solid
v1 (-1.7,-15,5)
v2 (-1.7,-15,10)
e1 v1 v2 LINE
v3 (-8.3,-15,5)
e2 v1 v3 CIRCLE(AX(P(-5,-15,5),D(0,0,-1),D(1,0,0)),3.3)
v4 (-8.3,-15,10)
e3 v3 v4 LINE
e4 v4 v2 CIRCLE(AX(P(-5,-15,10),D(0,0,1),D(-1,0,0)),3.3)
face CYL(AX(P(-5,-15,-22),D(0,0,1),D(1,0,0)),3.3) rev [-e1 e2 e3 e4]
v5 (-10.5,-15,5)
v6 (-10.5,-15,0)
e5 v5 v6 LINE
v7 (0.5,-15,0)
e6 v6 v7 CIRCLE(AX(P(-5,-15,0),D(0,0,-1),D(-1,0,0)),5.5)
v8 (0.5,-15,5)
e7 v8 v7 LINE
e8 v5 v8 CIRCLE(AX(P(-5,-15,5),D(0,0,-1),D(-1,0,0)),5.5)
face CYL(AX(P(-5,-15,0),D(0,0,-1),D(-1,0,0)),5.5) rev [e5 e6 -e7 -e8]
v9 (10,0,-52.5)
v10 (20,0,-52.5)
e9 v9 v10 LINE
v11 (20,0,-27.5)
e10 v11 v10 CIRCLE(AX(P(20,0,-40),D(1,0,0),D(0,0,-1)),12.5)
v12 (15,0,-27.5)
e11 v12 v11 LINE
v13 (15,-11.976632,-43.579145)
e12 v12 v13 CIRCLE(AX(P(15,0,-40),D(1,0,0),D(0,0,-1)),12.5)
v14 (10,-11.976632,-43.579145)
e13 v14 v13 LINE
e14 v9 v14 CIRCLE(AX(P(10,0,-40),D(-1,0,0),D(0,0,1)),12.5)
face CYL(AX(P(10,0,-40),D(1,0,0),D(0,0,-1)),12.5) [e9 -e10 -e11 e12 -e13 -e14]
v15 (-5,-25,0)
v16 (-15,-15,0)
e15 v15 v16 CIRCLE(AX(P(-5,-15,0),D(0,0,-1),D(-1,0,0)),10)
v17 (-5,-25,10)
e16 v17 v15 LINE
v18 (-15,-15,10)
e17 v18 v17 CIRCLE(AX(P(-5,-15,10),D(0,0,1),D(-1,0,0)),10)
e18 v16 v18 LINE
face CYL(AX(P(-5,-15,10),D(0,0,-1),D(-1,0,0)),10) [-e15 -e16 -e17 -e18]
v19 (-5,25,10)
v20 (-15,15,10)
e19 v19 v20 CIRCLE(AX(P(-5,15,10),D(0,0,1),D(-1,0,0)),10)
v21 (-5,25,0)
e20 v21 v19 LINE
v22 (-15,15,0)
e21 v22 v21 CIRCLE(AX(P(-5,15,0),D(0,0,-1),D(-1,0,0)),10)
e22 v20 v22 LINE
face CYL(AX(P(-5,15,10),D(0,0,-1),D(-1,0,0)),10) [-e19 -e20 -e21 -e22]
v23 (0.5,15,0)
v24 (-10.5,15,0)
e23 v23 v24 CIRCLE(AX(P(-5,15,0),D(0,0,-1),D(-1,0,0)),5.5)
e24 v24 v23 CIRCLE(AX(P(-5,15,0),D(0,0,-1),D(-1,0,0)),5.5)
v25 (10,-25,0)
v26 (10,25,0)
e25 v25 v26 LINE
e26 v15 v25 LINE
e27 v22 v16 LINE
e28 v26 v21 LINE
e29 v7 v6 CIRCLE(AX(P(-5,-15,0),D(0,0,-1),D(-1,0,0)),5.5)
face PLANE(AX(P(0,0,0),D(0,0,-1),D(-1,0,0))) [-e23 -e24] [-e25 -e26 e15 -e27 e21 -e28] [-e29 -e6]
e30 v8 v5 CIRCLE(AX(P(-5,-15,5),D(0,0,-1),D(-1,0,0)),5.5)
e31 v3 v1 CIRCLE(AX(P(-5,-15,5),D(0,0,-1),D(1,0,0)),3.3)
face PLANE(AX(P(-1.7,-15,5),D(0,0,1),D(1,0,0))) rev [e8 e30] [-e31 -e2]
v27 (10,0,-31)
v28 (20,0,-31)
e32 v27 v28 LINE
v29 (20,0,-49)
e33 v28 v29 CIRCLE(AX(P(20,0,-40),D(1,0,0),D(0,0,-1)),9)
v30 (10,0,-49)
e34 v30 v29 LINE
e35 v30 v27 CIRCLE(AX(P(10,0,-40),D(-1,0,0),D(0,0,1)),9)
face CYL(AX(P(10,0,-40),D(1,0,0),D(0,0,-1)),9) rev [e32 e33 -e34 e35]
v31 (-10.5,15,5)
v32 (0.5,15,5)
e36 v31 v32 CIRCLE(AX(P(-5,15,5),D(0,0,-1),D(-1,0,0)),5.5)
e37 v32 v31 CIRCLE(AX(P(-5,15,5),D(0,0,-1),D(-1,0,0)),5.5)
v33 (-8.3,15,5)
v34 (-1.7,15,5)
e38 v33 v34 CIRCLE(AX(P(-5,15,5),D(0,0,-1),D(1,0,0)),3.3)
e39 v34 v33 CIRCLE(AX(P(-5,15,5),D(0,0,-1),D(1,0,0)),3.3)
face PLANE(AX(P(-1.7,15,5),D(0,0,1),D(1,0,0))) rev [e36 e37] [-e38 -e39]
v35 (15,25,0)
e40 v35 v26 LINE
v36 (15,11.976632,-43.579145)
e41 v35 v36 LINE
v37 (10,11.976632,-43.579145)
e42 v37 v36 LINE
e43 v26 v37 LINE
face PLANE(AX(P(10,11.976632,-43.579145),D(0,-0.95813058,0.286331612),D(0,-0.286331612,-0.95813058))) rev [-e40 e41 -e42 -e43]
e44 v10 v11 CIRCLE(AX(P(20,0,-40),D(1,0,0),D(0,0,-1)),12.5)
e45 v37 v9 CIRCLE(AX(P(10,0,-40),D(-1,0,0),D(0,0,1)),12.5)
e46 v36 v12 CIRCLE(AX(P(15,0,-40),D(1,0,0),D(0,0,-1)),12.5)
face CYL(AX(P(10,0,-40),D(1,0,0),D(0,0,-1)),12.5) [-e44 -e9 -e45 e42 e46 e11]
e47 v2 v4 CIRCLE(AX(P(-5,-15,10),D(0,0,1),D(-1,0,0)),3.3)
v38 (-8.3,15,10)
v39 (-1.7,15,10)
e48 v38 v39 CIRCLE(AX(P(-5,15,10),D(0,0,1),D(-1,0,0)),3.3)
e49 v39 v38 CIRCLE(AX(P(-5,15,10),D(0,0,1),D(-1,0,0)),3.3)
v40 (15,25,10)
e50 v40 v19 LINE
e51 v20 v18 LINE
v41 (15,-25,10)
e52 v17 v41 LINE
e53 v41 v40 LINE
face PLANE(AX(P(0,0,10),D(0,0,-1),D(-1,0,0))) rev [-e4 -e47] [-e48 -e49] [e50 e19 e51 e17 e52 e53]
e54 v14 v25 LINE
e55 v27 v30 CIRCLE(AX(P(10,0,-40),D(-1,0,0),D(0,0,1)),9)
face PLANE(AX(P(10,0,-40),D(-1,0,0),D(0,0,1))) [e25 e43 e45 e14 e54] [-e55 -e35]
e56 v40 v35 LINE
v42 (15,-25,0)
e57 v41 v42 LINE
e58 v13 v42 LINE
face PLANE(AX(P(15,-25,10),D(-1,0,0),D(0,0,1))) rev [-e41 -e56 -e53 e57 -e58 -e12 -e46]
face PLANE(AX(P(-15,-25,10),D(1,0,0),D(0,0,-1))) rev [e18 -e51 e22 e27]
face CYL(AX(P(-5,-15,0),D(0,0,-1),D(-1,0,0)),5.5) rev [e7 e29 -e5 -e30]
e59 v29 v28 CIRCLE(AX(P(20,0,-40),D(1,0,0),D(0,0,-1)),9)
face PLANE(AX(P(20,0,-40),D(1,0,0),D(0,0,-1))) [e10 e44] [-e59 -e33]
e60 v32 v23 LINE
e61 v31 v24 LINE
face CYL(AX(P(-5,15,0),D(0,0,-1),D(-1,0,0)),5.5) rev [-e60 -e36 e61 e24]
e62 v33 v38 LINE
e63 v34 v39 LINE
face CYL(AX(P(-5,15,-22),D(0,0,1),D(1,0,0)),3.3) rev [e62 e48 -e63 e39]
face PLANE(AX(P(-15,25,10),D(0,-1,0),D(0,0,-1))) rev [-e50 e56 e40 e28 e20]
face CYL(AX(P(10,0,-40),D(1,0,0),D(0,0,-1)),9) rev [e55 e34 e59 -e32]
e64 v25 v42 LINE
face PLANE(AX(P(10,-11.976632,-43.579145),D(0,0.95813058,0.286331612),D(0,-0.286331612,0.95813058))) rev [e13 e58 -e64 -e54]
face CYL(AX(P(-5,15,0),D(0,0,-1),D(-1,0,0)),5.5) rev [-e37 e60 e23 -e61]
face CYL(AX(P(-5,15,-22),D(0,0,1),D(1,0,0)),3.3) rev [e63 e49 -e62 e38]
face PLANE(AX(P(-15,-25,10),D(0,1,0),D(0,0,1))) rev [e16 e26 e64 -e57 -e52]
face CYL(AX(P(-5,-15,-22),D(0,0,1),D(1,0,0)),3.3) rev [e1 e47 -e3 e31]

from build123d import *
from build123d.topology import SkipClean

# Parameters (mm, degrees)
SKETCH1_W                                    = 30
SKETCH1_H                                    = 50
BOSS_EXTRUDE1_DEPTH                          = 10
SKETCH2_R                                    = 9
BOSS_EXTRUDE3_DEPTH                          = 5
BOSS_EXTRUDE4_START                          = 5
SKETCH3_R                                    = 12.5
SKETCH3_R_2                                  = 9
BOSS_EXTRUDE4_DEPTH                          = 5
FILLET1_R                                    = 10
CBORE_FOR_M6_HEXAGON_SOCKET_HEAD_CAP_2_COUNT = 2
CBORE_FOR_M6_HEXAGON_SOCKET_HEAD_CAP_2_PITCH = 30
CUT_EXTRUDE1_DEPTH                           = 27
CUT_EXTRUDE1_DEPTH_BACK                      = 19
SKETCH8_R                                    = 3.3


with BuildPart() as part:
    # Sketch1 → Boss-Extrude1 (new body)
    with BuildSketch(Plane.XY):
        Rectangle(SKETCH1_W, SKETCH1_H)
    extrude(amount=BOSS_EXTRUDE1_DEPTH)

    # Sketch2 → Boss-Extrude3 (add)
    with BuildSketch(Plane(origin=(15, -15, 0), x_dir=(0, 1, 0), z_dir=(-1, 0, 0))):
        with BuildLine():
            Line((3.023367754, 43.579145154), (-10, 0))
            Line((-10, 0), (40, 0))
            Line((40, 0), (26.976632246, 43.579145154))
            ThreePointArc((26.976632246, 43.579145154), (15, 52.5), (3.023367754, 43.579145154))
        make_face()
        with Locations(Location((15, 40, 0), (0, 0, 270))):
            Circle(SKETCH2_R, mode=Mode.SUBTRACT)
    extrude(amount=BOSS_EXTRUDE3_DEPTH)

    # Sketch3 → Boss-Extrude4 (add)
    with SkipClean():  # the faces are left unmerged after this step: merging them gives an invalid solid
        with BuildSketch(Plane(origin=(15, 0, 0), x_dir=(0, 0, -1), z_dir=(1, 0, 0)).offset(BOSS_EXTRUDE4_START)):
            with Locations((40, 0)):
                Circle(SKETCH3_R)
            with Locations((40, 0)):
                Circle(SKETCH3_R_2, mode=Mode.SUBTRACT)
        extrude(amount=-BOSS_EXTRUDE4_DEPTH)

    # Fillet1
    fillet1_edges = [part.edges().sort_by_distance(p)[0] for p in [
        (-15, -25, 5),
        (-15, 25, 5),
    ]]
    fillet(fillet1_edges, radius=FILLET1_R)

    # Sketch4 → CBORE for M6 Hexagon socket head cap screws1 (revolve, cut)
    with BuildSketch(Plane(origin=(-5, -15, 0), x_dir=(0, 1, 0), z_dir=(1, 0, 0))):
        Polygon((0, 0), (0, 5), (3.3, 3.017159957), (3.3, 5), (5.5, 5), (5.5, 0), align=None)
    cbore_for_m6_hexagon_socket_head_cap_scr = revolve(axis=Axis((-5, -15, -6.35), (0, 0, 1)), mode=Mode.SUBTRACT)

    # CBORE for M6 Hexagon socket head cap 2: CBORE for M6 Hexagon socket head cap screws1 ×2
    with Locations(*[(0, i * CBORE_FOR_M6_HEXAGON_SOCKET_HEAD_CAP_2_PITCH, 0) for i in range(1, CBORE_FOR_M6_HEXAGON_SOCKET_HEAD_CAP_2_COUNT)]):
        add(cbore_for_m6_hexagon_socket_head_cap_scr, mode=Mode.SUBTRACT)

    # Sketch8 → Cut-Extrude1 (cut, two sides: drawn at the far end of the back side and taken through both)
    with BuildSketch(Plane(origin=(0, 0, 5), x_dir=(-1, 0, 0), z_dir=(0, 0, -1)).offset(-CUT_EXTRUDE1_DEPTH_BACK)):
        with Locations(Location((5, -15, 0), (0, 0, 180))):
            Circle(SKETCH8_R)
        with Locations(Location((5, 15, 0), (0, 0, 180))):
            Circle(SKETCH8_R)
    extrude(amount=CUT_EXTRUDE1_DEPTH + CUT_EXTRUDE1_DEPTH_BACK, mode=Mode.SUBTRACT)


solid = part.part
